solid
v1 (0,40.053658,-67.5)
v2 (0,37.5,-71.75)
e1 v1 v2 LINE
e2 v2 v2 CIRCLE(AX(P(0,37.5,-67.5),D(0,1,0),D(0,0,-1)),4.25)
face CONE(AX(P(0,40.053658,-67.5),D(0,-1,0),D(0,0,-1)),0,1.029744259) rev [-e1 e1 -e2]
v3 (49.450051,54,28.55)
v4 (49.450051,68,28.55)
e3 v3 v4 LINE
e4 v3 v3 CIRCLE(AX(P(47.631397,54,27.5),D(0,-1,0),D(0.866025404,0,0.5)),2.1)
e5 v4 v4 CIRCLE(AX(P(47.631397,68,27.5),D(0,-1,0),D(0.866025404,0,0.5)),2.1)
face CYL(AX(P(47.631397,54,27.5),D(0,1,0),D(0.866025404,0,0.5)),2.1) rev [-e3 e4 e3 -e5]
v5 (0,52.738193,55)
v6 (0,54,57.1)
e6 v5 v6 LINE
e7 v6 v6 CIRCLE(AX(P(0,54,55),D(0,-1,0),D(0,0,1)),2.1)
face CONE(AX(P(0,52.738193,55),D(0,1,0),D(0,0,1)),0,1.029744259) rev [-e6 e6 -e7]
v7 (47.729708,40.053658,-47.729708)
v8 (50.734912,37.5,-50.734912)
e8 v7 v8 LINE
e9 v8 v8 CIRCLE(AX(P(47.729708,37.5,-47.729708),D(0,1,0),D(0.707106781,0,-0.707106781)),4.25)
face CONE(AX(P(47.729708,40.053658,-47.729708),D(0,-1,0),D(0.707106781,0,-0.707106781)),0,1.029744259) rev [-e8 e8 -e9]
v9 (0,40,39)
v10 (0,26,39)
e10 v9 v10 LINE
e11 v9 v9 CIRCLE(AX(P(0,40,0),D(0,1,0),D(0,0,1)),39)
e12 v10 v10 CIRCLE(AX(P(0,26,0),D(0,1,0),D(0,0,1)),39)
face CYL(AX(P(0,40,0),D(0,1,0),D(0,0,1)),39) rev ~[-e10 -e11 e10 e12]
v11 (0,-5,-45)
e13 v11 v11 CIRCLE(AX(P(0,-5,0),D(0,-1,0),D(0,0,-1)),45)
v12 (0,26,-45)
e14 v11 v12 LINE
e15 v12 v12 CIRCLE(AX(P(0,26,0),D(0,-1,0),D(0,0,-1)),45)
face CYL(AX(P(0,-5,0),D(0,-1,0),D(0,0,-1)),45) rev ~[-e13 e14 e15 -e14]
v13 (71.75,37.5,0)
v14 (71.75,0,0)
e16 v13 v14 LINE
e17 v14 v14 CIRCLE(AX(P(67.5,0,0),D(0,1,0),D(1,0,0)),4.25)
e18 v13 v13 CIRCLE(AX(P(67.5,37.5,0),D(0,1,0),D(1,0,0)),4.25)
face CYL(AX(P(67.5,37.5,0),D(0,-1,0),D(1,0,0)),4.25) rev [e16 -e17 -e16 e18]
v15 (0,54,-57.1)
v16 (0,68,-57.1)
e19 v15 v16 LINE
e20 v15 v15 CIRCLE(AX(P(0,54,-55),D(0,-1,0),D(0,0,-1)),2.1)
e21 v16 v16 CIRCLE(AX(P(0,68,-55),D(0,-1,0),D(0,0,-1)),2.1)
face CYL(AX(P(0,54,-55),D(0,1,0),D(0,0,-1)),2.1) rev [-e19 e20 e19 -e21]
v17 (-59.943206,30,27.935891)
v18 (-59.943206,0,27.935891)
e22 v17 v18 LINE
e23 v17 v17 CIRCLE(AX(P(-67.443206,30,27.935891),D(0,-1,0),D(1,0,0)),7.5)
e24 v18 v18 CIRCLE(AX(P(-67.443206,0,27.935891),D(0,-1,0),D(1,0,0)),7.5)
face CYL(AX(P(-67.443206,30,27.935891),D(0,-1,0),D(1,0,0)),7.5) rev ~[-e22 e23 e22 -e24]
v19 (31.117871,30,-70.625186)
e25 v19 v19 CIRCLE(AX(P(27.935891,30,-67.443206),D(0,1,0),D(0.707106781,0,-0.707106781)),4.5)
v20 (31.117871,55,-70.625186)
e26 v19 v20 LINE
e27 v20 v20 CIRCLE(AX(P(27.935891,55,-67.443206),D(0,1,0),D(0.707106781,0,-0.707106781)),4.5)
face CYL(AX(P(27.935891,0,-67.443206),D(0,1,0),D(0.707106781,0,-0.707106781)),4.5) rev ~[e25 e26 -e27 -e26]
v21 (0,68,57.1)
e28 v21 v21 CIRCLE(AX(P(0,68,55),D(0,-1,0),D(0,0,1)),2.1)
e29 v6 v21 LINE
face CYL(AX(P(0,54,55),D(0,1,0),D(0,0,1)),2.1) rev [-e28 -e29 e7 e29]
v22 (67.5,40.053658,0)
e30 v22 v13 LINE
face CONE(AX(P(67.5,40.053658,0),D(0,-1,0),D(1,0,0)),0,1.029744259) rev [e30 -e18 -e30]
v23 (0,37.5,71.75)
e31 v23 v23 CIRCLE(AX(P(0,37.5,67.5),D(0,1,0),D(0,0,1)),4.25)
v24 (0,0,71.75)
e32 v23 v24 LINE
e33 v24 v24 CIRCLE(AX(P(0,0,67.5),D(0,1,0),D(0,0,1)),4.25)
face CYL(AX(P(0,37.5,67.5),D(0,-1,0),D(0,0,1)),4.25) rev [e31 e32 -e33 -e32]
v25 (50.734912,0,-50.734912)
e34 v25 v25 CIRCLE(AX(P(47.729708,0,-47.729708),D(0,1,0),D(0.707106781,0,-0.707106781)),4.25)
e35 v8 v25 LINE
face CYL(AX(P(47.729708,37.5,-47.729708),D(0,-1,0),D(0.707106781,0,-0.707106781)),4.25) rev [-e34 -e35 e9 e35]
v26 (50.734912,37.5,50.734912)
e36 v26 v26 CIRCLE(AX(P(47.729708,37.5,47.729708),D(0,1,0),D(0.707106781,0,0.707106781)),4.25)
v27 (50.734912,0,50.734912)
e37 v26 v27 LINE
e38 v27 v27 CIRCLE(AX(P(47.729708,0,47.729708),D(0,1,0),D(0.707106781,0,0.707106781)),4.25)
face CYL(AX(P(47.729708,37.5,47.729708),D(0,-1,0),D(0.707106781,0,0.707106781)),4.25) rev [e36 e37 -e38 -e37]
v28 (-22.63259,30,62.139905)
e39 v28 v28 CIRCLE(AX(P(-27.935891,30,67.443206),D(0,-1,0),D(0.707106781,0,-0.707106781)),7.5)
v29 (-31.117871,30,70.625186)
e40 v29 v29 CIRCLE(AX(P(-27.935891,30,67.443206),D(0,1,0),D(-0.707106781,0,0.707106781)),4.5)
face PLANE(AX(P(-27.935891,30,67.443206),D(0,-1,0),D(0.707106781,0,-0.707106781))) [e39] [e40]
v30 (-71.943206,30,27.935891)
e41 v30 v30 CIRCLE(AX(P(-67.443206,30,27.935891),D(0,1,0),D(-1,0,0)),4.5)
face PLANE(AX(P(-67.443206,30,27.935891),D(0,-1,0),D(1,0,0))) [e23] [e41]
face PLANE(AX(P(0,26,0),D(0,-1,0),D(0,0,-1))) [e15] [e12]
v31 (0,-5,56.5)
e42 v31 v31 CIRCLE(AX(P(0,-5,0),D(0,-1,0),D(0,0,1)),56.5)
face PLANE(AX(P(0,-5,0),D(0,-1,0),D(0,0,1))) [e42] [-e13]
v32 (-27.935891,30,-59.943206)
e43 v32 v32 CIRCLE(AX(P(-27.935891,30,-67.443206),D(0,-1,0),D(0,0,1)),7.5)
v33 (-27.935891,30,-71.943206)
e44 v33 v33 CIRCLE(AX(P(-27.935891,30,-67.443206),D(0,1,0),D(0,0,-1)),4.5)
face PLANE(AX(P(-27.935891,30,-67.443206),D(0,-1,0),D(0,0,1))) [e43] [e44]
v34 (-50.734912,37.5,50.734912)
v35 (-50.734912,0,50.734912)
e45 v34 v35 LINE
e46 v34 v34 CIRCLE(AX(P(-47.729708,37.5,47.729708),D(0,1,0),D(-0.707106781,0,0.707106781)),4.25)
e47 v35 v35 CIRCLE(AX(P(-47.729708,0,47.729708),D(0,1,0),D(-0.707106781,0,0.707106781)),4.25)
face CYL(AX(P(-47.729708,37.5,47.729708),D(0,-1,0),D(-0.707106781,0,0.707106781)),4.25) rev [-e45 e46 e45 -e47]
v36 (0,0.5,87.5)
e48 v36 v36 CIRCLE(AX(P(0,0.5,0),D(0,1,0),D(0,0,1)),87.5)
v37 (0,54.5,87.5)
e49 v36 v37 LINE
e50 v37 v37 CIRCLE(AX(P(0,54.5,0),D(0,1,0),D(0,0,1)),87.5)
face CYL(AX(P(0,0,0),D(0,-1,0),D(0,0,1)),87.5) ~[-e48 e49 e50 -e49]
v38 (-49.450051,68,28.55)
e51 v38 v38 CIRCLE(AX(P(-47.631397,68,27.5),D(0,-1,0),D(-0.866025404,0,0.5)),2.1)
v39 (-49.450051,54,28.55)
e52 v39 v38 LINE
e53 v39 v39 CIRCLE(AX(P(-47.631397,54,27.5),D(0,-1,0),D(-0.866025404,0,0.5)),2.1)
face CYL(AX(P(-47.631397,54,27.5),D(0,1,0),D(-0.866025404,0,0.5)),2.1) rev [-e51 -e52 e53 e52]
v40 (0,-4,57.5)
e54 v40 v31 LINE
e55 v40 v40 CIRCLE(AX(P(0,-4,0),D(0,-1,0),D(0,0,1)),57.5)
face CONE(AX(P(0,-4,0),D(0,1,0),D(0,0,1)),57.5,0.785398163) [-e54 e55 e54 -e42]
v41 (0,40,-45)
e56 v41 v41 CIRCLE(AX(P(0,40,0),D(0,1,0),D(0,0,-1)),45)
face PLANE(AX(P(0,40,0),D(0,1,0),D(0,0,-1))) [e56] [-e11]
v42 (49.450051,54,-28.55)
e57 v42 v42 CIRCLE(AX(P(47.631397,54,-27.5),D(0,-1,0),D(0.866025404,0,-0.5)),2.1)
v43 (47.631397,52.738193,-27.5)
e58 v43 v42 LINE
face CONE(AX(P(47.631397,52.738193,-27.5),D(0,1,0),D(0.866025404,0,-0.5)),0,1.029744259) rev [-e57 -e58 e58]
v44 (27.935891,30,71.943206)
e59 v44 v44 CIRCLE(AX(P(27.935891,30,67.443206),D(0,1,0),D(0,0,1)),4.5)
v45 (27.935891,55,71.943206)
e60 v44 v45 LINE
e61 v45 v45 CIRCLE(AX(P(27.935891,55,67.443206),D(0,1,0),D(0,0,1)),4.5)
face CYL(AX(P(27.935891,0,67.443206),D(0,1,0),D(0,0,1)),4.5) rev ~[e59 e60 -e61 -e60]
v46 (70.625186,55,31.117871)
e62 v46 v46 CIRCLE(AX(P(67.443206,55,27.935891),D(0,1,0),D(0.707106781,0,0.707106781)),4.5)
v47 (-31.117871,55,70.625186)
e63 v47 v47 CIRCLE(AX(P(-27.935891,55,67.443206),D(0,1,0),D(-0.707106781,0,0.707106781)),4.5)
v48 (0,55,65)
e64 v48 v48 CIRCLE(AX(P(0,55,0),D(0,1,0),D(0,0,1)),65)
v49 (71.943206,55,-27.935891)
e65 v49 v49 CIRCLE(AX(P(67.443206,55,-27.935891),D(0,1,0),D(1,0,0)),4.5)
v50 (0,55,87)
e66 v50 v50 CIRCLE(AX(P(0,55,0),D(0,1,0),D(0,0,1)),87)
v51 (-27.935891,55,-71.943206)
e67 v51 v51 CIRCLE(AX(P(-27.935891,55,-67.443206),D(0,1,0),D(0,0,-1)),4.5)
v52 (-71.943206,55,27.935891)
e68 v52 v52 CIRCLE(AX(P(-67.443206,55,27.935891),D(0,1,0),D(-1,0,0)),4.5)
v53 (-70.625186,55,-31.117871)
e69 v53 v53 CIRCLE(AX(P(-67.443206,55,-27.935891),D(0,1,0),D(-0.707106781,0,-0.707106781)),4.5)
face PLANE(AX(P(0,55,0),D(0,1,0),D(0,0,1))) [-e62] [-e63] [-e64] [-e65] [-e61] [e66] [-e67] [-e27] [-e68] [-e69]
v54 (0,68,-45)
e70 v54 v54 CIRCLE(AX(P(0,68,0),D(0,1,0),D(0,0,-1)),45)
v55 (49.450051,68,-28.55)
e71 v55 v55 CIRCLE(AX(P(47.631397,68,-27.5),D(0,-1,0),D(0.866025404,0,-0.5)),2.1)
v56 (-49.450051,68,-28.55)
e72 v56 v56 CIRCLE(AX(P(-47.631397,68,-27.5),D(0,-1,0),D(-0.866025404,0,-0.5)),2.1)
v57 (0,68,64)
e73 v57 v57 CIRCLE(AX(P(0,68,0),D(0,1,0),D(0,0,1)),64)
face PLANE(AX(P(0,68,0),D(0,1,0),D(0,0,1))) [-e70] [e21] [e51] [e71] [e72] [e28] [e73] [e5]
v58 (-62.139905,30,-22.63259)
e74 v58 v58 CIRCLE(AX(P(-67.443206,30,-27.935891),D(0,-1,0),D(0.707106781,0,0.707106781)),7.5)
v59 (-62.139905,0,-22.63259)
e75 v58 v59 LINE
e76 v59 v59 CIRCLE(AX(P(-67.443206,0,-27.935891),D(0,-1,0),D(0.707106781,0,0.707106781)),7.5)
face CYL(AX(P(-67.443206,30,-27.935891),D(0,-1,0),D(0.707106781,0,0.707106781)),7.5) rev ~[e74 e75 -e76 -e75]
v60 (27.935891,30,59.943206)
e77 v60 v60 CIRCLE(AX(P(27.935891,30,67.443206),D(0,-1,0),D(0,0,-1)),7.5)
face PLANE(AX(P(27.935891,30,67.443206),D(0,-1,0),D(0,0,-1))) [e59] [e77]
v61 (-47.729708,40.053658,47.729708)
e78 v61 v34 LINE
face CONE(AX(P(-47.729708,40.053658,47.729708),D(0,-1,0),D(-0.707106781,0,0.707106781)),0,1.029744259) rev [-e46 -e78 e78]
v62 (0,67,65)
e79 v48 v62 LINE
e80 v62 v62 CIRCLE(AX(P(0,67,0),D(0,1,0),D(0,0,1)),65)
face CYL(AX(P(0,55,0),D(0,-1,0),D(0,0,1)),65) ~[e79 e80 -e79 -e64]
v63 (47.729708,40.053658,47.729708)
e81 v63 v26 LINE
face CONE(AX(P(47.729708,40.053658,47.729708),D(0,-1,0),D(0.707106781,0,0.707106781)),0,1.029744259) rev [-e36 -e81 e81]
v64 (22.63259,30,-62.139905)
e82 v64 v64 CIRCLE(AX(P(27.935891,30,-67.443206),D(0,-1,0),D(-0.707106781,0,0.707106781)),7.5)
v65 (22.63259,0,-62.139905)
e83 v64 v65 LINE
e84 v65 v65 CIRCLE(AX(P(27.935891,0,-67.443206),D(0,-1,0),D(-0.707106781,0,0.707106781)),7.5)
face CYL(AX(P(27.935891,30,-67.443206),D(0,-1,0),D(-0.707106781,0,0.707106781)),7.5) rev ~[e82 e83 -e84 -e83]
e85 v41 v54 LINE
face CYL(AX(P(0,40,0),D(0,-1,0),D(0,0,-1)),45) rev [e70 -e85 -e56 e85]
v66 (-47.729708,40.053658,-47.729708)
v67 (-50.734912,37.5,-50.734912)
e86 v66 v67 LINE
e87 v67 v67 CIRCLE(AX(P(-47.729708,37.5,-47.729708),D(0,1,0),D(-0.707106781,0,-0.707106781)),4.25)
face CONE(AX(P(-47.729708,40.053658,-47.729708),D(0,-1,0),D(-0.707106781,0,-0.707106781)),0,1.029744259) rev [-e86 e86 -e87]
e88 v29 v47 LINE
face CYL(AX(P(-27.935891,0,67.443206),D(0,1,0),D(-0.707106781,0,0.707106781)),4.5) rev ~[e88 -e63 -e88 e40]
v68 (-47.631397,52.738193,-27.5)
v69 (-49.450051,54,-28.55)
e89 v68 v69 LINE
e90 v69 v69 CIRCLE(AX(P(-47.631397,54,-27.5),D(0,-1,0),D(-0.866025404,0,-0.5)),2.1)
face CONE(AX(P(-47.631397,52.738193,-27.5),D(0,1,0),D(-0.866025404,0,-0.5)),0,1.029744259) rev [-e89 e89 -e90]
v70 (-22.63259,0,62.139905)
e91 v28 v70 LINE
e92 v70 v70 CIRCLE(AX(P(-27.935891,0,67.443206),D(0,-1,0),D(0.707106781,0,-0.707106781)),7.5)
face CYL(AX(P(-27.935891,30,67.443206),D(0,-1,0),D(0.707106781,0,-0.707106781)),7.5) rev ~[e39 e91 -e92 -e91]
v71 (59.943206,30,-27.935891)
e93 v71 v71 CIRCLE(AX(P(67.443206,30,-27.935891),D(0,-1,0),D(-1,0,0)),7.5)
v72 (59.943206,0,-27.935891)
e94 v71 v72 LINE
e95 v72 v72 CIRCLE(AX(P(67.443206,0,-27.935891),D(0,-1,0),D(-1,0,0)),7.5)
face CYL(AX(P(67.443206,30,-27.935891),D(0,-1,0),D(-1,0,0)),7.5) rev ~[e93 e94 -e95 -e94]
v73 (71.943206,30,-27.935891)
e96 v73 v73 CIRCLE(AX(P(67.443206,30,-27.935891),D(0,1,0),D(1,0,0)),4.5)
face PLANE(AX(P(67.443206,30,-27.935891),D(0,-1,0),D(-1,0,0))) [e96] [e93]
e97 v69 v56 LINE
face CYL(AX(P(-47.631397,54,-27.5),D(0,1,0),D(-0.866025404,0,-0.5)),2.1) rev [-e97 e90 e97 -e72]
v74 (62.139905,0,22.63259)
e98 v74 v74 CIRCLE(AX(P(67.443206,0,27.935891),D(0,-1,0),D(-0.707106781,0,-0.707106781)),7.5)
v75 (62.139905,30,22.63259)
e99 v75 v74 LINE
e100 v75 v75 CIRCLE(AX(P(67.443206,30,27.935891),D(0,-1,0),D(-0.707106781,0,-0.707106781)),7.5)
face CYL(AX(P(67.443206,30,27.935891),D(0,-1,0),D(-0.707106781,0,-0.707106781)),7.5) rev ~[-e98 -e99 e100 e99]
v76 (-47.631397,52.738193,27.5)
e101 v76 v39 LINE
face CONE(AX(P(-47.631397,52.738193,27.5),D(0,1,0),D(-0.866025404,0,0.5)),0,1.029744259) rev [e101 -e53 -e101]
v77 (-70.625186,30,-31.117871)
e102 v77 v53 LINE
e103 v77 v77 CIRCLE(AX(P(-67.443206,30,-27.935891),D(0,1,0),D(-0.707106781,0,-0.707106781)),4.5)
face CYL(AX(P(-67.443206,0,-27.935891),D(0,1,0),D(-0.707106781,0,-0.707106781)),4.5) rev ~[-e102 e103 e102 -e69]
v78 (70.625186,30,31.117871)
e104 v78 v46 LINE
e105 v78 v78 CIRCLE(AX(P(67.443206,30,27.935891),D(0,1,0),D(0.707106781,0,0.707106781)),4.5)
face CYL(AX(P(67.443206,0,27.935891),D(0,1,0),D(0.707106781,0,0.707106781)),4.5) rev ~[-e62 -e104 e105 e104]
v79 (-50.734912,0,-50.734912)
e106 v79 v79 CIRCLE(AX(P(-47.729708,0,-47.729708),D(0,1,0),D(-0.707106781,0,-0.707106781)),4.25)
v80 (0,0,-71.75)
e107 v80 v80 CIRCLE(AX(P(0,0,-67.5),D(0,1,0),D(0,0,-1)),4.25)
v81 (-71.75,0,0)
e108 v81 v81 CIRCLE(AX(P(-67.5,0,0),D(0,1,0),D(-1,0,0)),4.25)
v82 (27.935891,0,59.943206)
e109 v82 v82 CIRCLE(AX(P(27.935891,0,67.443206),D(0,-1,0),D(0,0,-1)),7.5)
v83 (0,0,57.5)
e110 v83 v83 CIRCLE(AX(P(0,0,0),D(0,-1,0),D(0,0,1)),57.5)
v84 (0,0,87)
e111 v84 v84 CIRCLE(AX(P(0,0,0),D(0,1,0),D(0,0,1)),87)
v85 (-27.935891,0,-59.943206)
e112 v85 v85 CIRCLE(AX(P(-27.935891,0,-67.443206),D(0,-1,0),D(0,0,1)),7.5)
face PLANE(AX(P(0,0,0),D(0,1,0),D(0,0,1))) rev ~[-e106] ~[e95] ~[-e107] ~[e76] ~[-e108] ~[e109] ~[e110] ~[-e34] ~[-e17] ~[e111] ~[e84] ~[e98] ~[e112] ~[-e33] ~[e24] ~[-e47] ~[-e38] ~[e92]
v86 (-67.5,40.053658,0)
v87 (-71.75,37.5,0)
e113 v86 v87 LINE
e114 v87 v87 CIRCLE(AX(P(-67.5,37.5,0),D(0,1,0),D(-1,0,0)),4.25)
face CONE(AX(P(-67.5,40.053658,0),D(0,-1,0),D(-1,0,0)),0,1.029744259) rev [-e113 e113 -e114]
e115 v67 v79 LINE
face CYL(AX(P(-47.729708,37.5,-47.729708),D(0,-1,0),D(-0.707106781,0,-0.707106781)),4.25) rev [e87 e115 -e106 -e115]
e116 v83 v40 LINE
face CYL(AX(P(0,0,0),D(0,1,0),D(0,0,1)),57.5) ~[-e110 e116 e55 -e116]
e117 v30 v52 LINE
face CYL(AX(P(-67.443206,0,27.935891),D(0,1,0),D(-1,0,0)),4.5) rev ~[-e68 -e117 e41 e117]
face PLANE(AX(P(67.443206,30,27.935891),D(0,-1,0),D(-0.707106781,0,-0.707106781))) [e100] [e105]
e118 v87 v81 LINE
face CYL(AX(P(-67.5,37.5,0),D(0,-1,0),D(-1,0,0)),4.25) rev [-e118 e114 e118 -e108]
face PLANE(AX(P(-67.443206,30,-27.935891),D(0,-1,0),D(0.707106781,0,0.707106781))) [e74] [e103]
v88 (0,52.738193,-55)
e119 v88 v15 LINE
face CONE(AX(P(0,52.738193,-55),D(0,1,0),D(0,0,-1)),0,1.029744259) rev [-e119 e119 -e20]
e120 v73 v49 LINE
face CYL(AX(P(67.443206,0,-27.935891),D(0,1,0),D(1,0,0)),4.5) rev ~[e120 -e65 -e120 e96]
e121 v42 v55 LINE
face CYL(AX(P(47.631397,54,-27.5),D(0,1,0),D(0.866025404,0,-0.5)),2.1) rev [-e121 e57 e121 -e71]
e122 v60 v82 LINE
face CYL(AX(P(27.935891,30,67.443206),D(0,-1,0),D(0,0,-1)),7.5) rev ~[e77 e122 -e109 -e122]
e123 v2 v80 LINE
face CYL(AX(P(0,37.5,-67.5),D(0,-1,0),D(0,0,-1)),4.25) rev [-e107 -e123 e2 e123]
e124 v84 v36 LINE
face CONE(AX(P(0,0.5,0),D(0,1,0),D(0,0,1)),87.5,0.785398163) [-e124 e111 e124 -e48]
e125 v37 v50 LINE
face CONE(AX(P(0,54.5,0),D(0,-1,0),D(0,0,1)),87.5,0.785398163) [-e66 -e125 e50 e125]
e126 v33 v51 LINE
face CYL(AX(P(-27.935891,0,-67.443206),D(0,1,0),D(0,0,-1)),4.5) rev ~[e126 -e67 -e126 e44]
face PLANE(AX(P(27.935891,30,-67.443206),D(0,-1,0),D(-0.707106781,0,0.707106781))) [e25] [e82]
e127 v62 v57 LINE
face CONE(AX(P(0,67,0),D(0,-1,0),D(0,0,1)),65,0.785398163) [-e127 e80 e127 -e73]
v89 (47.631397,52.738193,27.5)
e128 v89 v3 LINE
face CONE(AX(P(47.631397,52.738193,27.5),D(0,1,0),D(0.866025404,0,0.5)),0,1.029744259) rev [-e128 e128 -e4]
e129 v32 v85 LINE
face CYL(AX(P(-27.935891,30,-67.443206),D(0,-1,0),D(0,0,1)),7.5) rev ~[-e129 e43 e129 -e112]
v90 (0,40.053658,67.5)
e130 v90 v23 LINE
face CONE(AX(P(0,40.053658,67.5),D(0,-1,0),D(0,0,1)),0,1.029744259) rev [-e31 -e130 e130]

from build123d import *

# Parameters (mm, degrees)
SKETCH1_R                                          = 87.5
BOSS_EXTRUDE1_DEPTH                                = 55
SKETCH2_R                                          = 65
BOSS_EXTRUDE2_DEPTH                                = 13
SKETCH3_R                                          = 57.5
BOSS_EXTRUDE3_DEPTH                                = 5
SKETCH4_R                                          = 45
CUT_EXTRUDE1_DEPTH                                 = 31
CUT_EXTRUDE2_START                                 = -28
SKETCH5_R                                          = 45
CUT_EXTRUDE2_DEPTH                                 = 28
SKETCH6_R                                          = 39
CUT_EXTRUDE3_DEPTH                                 = 132.671940823
CHAMFER1_SIZE                                      = 1
HOLE_SIZE_BASED_ON_SOCKET_HEAD_CAP_SCR_D           = 9
HOLE_SIZE_BASED_ON_SOCKET_HEAD_CAP_SCR_CBORE_D     = 15
HOLE_SIZE_BASED_ON_SOCKET_HEAD_CAP_SCR_CBORE_DEPTH = 30
CIRPATTERN1_COUNT                                  = 8
CHAMFER2_SIZE                                      = 0.5
CIRPATTERN2_COUNT                                  = 8
CIRPATTERN3_COUNT                                  = 6


with BuildPart() as part:
    # Sketch1 → Boss-Extrude1 (new body)
    with BuildSketch(Plane(origin=(0, 0, 0), x_dir=(1, 0, 0), z_dir=(0, 1, 0))):
        with Locations(Location((0, 0, 0), (0, 0, 270))):
            Circle(SKETCH1_R)
    extrude(amount=BOSS_EXTRUDE1_DEPTH)

    # Sketch2 → Boss-Extrude2 (add)
    with BuildSketch(Plane(origin=(0, 55, 0), x_dir=(1, 0, 0), z_dir=(0, 1, 0))):
        with Locations(Location((0, 0, 0), (0, 0, 270))):
            Circle(SKETCH2_R)
    extrude(amount=BOSS_EXTRUDE2_DEPTH)

    # Sketch3 → Boss-Extrude3 (add)
    with BuildSketch(Plane.XZ):
        with Locations(Location((0, 0, 0), (0, 0, 90))):
            Circle(SKETCH3_R)
    extrude(amount=BOSS_EXTRUDE3_DEPTH)

    # Sketch4 → Cut-Extrude1 (cut)
    with BuildSketch(Plane.XZ.offset(5)):
        with Locations(Location((0, 0, 0), (0, 0, 270))):
            Circle(SKETCH4_R)
    extrude(amount=-CUT_EXTRUDE1_DEPTH, mode=Mode.SUBTRACT)

    # Sketch5 → Cut-Extrude2 (cut)
    with BuildSketch(Plane(origin=(0, 68, 0), x_dir=(1, 0, 0), z_dir=(0, 1, 0)).offset(CUT_EXTRUDE2_START)):
        with Locations(Location((0, 0, 0), (0, 0, 90))):
            Circle(SKETCH5_R)
    extrude(amount=CUT_EXTRUDE2_DEPTH, mode=Mode.SUBTRACT)

    # Sketch6 → Cut-Extrude3 (cut, through all)
    with BuildSketch(Plane(origin=(0, 40, 0), x_dir=(1, 0, 0), z_dir=(0, 1, 0))):
        with Locations(Location((0, 0, 0), (0, 0, 270))):
            Circle(SKETCH6_R)
    extrude(amount=-CUT_EXTRUDE3_DEPTH, mode=Mode.SUBTRACT)

    # Chamfer1
    chamfer1_edges = [part.edges().sort_by_distance(p)[0] for p in [
        (0, -5, -57.5),
        (0, 68, -65),
    ]]
    chamfer(chamfer1_edges, length=CHAMFER1_SIZE)

    # Hole size (% based on socket head cap screw type)1 (through all)
    with Locations(Plane(origin=(0, 0, 0), x_dir=(-1, 0, 0), z_dir=(0, -1, 0))):
        with Locations((-67.443205873, 27.935890563)):
            hole_size_based_on_socket_head_cap_scr = CounterBoreHole(HOLE_SIZE_BASED_ON_SOCKET_HEAD_CAP_SCR_D / 2, HOLE_SIZE_BASED_ON_SOCKET_HEAD_CAP_SCR_CBORE_D / 2, HOLE_SIZE_BASED_ON_SOCKET_HEAD_CAP_SCR_CBORE_DEPTH)

    # CirPattern1: Hole size (% based on socket head cap screw type)1 ×8 about axis
    cirpattern1_axis = Axis((0, 0, 0), (0, 1, 0))
    for i in range(1, CIRPATTERN1_COUNT):
        add(hole_size_based_on_socket_head_cap_scr.rotate(cirpattern1_axis, i * 360 / CIRPATTERN1_COUNT), mode=Mode.SUBTRACT)

    # Chamfer2
    chamfer2_edges = [part.edges().sort_by_distance(p)[0] for p in [
        (0, 0, -87.5),
        (0, 55, -87.5),
    ]]
    chamfer(chamfer2_edges, length=CHAMFER2_SIZE)

    # Sketch13 → M10 Tapped Hole1 (revolve, cut)
    with BuildSketch(Plane(origin=(0, 0, -67.5), x_dir=(0, 0, -1), z_dir=(1, 0, 0))):
        Polygon((0, 0), (0, 40.053657631), (4.25, 37.5), (4.25, 0), align=None)
    m10_tapped_hole1 = revolve(axis=Axis((0, -6.35, -67.5), (0, 1, 0)), mode=Mode.SUBTRACT)

    # CirPattern2: M10 Tapped Hole1 ×8 about axis
    cirpattern2_axis = Axis((0, 0, 0), (0, 1, 0))
    for i in range(1, CIRPATTERN2_COUNT):
        add(m10_tapped_hole1.rotate(cirpattern2_axis, i * 360 / CIRPATTERN2_COUNT), mode=Mode.SUBTRACT)

    # Sketch15 → M5 Tapped Hole1 (revolve, cut)
    with BuildSketch(Plane(origin=(0, 68, 55), x_dir=(0, 0, 1), z_dir=(1, 0, 0))):
        Polygon((0, 0), (0, 15.2618073), (2.1, 14), (2.1, 0), align=None)
    m5_tapped_hole1 = revolve(axis=Axis((0, 74.35, 55), (0, -1, 0)), mode=Mode.SUBTRACT)

    # CirPattern3: M5 Tapped Hole1 ×6 about axis
    cirpattern3_axis = Axis((0, 0, 0), (0, 1, 0))
    for i in range(1, CIRPATTERN3_COUNT):
        add(m5_tapped_hole1.rotate(cirpattern3_axis, i * 360 / CIRPATTERN3_COUNT), mode=Mode.SUBTRACT)


solid = part.part
